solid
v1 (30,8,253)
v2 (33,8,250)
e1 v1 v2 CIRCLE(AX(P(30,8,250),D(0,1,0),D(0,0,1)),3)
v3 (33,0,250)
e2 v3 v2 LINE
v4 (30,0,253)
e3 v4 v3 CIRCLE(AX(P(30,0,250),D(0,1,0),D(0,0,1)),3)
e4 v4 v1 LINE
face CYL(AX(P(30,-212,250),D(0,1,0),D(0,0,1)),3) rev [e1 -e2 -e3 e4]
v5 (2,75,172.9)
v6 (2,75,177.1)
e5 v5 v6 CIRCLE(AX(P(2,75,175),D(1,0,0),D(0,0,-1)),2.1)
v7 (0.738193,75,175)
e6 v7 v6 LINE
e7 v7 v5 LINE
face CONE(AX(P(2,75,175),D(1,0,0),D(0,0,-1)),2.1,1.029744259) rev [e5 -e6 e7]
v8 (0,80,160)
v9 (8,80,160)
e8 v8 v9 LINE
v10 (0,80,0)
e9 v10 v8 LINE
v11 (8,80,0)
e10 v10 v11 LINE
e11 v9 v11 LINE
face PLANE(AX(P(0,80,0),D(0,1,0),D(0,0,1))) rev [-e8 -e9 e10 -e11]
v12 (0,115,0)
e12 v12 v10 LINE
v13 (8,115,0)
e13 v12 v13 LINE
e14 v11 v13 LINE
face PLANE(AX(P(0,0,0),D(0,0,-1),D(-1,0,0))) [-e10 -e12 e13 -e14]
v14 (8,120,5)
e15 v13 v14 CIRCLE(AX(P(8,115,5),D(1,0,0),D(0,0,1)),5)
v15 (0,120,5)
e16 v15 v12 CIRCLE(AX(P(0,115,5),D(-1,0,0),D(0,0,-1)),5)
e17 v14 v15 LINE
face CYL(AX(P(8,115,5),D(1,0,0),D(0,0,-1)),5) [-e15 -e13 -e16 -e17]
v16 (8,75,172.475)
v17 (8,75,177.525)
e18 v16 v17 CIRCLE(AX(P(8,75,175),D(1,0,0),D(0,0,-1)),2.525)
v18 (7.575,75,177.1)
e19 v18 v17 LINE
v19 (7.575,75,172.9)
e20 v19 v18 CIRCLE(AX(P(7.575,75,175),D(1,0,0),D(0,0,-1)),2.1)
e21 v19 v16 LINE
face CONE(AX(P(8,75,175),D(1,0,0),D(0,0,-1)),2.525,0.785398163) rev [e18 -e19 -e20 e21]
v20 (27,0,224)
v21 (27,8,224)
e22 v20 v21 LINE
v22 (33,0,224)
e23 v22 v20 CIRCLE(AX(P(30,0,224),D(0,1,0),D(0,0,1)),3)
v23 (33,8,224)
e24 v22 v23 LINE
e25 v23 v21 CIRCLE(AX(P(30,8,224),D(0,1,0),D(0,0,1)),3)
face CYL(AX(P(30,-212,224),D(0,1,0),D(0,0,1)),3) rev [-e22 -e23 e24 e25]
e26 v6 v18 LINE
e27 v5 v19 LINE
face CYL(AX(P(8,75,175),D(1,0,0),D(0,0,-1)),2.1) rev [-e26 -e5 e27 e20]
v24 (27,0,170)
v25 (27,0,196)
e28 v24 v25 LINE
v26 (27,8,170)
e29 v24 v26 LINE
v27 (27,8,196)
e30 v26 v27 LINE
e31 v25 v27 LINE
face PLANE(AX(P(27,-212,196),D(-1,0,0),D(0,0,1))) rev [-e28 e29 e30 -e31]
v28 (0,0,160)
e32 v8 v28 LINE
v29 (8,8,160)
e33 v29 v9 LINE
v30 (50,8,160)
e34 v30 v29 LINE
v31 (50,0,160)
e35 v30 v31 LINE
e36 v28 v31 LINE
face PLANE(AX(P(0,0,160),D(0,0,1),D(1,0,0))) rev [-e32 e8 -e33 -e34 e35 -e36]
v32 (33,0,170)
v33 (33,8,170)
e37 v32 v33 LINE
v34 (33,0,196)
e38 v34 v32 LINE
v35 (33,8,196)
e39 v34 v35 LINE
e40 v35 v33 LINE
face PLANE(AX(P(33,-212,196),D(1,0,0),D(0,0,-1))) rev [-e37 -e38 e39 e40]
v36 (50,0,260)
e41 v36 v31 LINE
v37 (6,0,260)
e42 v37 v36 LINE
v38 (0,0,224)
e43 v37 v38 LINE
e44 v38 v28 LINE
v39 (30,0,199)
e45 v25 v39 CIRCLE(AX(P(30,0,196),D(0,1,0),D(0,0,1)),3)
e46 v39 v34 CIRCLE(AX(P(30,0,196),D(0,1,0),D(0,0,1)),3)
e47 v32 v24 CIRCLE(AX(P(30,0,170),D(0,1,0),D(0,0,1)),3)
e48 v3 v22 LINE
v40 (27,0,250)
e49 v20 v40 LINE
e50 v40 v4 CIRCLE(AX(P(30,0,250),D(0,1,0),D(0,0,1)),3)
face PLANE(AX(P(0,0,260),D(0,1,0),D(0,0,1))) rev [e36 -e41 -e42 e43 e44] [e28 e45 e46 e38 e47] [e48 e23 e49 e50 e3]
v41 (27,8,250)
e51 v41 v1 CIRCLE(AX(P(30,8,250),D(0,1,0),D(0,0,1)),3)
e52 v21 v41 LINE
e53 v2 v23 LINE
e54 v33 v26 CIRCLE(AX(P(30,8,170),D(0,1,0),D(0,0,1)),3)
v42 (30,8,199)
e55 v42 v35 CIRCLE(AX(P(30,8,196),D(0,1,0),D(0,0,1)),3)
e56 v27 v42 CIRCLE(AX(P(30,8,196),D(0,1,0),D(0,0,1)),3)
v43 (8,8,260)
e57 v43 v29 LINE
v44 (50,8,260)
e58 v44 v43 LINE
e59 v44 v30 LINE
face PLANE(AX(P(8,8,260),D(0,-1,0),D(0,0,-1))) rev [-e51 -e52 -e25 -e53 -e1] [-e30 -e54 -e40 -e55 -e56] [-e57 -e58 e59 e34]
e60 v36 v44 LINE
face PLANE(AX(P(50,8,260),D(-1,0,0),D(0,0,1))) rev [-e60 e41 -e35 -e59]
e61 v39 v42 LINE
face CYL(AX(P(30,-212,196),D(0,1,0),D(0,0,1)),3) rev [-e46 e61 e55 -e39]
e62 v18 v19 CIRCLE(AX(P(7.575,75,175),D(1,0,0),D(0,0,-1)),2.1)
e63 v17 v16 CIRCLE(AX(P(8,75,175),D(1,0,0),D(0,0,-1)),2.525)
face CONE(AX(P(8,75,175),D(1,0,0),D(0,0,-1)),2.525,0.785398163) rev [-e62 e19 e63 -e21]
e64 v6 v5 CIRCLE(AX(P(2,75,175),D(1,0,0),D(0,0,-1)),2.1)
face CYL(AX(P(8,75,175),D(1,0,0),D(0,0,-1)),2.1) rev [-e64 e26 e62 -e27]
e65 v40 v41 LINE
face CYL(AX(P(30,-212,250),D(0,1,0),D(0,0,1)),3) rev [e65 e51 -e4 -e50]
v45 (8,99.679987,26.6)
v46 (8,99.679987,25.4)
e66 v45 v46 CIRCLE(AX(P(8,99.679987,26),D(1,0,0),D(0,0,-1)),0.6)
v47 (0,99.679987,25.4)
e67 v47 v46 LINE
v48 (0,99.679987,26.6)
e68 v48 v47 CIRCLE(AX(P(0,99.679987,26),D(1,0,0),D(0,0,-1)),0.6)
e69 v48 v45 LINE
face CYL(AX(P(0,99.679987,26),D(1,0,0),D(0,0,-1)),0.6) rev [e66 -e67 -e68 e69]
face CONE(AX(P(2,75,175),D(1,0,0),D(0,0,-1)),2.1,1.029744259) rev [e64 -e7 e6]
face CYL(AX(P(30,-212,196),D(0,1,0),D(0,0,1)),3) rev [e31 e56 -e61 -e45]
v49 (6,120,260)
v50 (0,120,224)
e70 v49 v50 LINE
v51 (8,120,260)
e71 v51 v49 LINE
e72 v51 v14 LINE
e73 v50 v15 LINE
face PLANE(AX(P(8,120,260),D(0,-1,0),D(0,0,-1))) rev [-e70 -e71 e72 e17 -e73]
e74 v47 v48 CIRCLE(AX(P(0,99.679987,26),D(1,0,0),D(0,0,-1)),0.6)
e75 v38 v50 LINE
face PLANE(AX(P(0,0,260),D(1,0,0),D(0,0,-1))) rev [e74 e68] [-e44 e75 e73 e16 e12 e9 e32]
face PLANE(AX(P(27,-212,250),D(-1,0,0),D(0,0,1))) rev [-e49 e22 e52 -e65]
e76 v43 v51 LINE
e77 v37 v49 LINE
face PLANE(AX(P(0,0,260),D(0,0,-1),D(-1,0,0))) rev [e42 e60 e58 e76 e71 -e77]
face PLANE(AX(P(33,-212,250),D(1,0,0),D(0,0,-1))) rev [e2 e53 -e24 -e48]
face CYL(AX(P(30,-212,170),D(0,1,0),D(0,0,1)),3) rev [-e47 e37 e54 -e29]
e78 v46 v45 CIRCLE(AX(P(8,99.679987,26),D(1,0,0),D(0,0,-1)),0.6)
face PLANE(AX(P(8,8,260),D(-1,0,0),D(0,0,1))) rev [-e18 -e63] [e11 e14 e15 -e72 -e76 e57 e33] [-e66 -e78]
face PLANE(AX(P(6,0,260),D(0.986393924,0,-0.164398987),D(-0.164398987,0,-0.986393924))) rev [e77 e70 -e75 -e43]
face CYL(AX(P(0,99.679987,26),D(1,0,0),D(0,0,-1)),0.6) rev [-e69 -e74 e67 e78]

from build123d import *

# Parameters (mm, degrees)
BOSS_EXTRUDE1_DEPTH         = 260
SKETCH2_W                   = 160
SKETCH2_H                   = 80
CUT_EXTRUDE1_DEPTH          = 291.688837075
CUT_EXTRUDE2_DEPTH          = 220
CUT_EXTRUDE3_DEPTH          = 291.688837075
M5_TAPPED_HOLE1_D           = 4.2
M5_TAPPED_HOLE1_DEPTH       = 6
M5_TAPPED_HOLE1_CSINK_D     = 5.05
M5_TAPPED_HOLE1_CSINK_ANGLE = 90
M5_TAPPED_HOLE1_TIP         = 1.2618073
FILLET1_R                   = 5
SKETCH6_R                   = 0.6
CUT_EXTRUDE4_DEPTH          = 290.420109875


with BuildPart() as part:
    # Sketch1 → Boss-Extrude1 (new body)
    with BuildSketch(Plane.XY):
        Polygon((0, 0), (0, 120), (8, 120), (8, 8), (50, 8), (50, 0), align=None)
    extrude(amount=BOSS_EXTRUDE1_DEPTH)

    # Sketch2 → Cut-Extrude1 (cut, through all)
    with BuildSketch(Plane(origin=(50, 0, 0), x_dir=(0, 0, -1), z_dir=(1, 0, 0))):
        with Locations((-80, 40)):
            Rectangle(SKETCH2_W, SKETCH2_H)
    extrude(amount=-CUT_EXTRUDE1_DEPTH, mode=Mode.SUBTRACT)

    # Sketch3 → Cut-Extrude2 (cut)
    with BuildSketch(Plane(origin=(0, 8, 0), x_dir=(1, 0, 0), z_dir=(0, 1, 0))):
        with BuildLine():
            Line((27, -250), (27, -224))
            ThreePointArc((27, -224), (30, -221), (33, -224))
            Line((33, -224), (33, -250))
            ThreePointArc((33, -250), (30, -253), (27, -250))
        make_face()
        with BuildLine():
            Line((27, -196), (27, -170))
            ThreePointArc((27, -170), (30, -167), (33, -170))
            Line((33, -170), (33, -196))
            ThreePointArc((33, -196), (30, -199), (27, -196))
        make_face()
    extrude(amount=-CUT_EXTRUDE2_DEPTH, mode=Mode.SUBTRACT)

    # Sketch4 → Cut-Extrude3 (cut, through all)
    with BuildSketch(Plane(origin=(0, 120, 0), x_dir=(1, 0, 0), z_dir=(0, 1, 0))):
        Polygon((6, -260), (0, -224), (0, -260), align=None)
    extrude(amount=-CUT_EXTRUDE3_DEPTH, mode=Mode.SUBTRACT)

    # M5 Tapped Hole1
    with Locations(Plane(origin=(8, 75, 175), x_dir=(0, 0, 1), z_dir=(1, 0, 0))):
        with Locations((0, 0)):
            CounterSinkHole(M5_TAPPED_HOLE1_D / 2, M5_TAPPED_HOLE1_CSINK_D / 2, depth=M5_TAPPED_HOLE1_DEPTH, counter_sink_angle=M5_TAPPED_HOLE1_CSINK_ANGLE)
            with Locations((0, 0, -(M5_TAPPED_HOLE1_DEPTH + M5_TAPPED_HOLE1_TIP / 2))):  # 118° drill point
                Cone(0, M5_TAPPED_HOLE1_D / 2, M5_TAPPED_HOLE1_TIP, mode=Mode.SUBTRACT)

    # Fillet1
    fillet1_edges = [part.edges().sort_by_distance(p)[0] for p in [
        (4, 120, 0),
    ]]
    fillet(fillet1_edges, radius=FILLET1_R)

    # Sketch6 → Cut-Extrude4 (cut, through all)
    with BuildSketch(Plane(origin=(8, 0, 0), x_dir=(0, 0, -1), z_dir=(1, 0, 0))):
        with Locations((-26, 99.679986911)):
            Circle(SKETCH6_R)
    extrude(amount=-CUT_EXTRUDE4_DEPTH, mode=Mode.SUBTRACT)


solid = part.part
